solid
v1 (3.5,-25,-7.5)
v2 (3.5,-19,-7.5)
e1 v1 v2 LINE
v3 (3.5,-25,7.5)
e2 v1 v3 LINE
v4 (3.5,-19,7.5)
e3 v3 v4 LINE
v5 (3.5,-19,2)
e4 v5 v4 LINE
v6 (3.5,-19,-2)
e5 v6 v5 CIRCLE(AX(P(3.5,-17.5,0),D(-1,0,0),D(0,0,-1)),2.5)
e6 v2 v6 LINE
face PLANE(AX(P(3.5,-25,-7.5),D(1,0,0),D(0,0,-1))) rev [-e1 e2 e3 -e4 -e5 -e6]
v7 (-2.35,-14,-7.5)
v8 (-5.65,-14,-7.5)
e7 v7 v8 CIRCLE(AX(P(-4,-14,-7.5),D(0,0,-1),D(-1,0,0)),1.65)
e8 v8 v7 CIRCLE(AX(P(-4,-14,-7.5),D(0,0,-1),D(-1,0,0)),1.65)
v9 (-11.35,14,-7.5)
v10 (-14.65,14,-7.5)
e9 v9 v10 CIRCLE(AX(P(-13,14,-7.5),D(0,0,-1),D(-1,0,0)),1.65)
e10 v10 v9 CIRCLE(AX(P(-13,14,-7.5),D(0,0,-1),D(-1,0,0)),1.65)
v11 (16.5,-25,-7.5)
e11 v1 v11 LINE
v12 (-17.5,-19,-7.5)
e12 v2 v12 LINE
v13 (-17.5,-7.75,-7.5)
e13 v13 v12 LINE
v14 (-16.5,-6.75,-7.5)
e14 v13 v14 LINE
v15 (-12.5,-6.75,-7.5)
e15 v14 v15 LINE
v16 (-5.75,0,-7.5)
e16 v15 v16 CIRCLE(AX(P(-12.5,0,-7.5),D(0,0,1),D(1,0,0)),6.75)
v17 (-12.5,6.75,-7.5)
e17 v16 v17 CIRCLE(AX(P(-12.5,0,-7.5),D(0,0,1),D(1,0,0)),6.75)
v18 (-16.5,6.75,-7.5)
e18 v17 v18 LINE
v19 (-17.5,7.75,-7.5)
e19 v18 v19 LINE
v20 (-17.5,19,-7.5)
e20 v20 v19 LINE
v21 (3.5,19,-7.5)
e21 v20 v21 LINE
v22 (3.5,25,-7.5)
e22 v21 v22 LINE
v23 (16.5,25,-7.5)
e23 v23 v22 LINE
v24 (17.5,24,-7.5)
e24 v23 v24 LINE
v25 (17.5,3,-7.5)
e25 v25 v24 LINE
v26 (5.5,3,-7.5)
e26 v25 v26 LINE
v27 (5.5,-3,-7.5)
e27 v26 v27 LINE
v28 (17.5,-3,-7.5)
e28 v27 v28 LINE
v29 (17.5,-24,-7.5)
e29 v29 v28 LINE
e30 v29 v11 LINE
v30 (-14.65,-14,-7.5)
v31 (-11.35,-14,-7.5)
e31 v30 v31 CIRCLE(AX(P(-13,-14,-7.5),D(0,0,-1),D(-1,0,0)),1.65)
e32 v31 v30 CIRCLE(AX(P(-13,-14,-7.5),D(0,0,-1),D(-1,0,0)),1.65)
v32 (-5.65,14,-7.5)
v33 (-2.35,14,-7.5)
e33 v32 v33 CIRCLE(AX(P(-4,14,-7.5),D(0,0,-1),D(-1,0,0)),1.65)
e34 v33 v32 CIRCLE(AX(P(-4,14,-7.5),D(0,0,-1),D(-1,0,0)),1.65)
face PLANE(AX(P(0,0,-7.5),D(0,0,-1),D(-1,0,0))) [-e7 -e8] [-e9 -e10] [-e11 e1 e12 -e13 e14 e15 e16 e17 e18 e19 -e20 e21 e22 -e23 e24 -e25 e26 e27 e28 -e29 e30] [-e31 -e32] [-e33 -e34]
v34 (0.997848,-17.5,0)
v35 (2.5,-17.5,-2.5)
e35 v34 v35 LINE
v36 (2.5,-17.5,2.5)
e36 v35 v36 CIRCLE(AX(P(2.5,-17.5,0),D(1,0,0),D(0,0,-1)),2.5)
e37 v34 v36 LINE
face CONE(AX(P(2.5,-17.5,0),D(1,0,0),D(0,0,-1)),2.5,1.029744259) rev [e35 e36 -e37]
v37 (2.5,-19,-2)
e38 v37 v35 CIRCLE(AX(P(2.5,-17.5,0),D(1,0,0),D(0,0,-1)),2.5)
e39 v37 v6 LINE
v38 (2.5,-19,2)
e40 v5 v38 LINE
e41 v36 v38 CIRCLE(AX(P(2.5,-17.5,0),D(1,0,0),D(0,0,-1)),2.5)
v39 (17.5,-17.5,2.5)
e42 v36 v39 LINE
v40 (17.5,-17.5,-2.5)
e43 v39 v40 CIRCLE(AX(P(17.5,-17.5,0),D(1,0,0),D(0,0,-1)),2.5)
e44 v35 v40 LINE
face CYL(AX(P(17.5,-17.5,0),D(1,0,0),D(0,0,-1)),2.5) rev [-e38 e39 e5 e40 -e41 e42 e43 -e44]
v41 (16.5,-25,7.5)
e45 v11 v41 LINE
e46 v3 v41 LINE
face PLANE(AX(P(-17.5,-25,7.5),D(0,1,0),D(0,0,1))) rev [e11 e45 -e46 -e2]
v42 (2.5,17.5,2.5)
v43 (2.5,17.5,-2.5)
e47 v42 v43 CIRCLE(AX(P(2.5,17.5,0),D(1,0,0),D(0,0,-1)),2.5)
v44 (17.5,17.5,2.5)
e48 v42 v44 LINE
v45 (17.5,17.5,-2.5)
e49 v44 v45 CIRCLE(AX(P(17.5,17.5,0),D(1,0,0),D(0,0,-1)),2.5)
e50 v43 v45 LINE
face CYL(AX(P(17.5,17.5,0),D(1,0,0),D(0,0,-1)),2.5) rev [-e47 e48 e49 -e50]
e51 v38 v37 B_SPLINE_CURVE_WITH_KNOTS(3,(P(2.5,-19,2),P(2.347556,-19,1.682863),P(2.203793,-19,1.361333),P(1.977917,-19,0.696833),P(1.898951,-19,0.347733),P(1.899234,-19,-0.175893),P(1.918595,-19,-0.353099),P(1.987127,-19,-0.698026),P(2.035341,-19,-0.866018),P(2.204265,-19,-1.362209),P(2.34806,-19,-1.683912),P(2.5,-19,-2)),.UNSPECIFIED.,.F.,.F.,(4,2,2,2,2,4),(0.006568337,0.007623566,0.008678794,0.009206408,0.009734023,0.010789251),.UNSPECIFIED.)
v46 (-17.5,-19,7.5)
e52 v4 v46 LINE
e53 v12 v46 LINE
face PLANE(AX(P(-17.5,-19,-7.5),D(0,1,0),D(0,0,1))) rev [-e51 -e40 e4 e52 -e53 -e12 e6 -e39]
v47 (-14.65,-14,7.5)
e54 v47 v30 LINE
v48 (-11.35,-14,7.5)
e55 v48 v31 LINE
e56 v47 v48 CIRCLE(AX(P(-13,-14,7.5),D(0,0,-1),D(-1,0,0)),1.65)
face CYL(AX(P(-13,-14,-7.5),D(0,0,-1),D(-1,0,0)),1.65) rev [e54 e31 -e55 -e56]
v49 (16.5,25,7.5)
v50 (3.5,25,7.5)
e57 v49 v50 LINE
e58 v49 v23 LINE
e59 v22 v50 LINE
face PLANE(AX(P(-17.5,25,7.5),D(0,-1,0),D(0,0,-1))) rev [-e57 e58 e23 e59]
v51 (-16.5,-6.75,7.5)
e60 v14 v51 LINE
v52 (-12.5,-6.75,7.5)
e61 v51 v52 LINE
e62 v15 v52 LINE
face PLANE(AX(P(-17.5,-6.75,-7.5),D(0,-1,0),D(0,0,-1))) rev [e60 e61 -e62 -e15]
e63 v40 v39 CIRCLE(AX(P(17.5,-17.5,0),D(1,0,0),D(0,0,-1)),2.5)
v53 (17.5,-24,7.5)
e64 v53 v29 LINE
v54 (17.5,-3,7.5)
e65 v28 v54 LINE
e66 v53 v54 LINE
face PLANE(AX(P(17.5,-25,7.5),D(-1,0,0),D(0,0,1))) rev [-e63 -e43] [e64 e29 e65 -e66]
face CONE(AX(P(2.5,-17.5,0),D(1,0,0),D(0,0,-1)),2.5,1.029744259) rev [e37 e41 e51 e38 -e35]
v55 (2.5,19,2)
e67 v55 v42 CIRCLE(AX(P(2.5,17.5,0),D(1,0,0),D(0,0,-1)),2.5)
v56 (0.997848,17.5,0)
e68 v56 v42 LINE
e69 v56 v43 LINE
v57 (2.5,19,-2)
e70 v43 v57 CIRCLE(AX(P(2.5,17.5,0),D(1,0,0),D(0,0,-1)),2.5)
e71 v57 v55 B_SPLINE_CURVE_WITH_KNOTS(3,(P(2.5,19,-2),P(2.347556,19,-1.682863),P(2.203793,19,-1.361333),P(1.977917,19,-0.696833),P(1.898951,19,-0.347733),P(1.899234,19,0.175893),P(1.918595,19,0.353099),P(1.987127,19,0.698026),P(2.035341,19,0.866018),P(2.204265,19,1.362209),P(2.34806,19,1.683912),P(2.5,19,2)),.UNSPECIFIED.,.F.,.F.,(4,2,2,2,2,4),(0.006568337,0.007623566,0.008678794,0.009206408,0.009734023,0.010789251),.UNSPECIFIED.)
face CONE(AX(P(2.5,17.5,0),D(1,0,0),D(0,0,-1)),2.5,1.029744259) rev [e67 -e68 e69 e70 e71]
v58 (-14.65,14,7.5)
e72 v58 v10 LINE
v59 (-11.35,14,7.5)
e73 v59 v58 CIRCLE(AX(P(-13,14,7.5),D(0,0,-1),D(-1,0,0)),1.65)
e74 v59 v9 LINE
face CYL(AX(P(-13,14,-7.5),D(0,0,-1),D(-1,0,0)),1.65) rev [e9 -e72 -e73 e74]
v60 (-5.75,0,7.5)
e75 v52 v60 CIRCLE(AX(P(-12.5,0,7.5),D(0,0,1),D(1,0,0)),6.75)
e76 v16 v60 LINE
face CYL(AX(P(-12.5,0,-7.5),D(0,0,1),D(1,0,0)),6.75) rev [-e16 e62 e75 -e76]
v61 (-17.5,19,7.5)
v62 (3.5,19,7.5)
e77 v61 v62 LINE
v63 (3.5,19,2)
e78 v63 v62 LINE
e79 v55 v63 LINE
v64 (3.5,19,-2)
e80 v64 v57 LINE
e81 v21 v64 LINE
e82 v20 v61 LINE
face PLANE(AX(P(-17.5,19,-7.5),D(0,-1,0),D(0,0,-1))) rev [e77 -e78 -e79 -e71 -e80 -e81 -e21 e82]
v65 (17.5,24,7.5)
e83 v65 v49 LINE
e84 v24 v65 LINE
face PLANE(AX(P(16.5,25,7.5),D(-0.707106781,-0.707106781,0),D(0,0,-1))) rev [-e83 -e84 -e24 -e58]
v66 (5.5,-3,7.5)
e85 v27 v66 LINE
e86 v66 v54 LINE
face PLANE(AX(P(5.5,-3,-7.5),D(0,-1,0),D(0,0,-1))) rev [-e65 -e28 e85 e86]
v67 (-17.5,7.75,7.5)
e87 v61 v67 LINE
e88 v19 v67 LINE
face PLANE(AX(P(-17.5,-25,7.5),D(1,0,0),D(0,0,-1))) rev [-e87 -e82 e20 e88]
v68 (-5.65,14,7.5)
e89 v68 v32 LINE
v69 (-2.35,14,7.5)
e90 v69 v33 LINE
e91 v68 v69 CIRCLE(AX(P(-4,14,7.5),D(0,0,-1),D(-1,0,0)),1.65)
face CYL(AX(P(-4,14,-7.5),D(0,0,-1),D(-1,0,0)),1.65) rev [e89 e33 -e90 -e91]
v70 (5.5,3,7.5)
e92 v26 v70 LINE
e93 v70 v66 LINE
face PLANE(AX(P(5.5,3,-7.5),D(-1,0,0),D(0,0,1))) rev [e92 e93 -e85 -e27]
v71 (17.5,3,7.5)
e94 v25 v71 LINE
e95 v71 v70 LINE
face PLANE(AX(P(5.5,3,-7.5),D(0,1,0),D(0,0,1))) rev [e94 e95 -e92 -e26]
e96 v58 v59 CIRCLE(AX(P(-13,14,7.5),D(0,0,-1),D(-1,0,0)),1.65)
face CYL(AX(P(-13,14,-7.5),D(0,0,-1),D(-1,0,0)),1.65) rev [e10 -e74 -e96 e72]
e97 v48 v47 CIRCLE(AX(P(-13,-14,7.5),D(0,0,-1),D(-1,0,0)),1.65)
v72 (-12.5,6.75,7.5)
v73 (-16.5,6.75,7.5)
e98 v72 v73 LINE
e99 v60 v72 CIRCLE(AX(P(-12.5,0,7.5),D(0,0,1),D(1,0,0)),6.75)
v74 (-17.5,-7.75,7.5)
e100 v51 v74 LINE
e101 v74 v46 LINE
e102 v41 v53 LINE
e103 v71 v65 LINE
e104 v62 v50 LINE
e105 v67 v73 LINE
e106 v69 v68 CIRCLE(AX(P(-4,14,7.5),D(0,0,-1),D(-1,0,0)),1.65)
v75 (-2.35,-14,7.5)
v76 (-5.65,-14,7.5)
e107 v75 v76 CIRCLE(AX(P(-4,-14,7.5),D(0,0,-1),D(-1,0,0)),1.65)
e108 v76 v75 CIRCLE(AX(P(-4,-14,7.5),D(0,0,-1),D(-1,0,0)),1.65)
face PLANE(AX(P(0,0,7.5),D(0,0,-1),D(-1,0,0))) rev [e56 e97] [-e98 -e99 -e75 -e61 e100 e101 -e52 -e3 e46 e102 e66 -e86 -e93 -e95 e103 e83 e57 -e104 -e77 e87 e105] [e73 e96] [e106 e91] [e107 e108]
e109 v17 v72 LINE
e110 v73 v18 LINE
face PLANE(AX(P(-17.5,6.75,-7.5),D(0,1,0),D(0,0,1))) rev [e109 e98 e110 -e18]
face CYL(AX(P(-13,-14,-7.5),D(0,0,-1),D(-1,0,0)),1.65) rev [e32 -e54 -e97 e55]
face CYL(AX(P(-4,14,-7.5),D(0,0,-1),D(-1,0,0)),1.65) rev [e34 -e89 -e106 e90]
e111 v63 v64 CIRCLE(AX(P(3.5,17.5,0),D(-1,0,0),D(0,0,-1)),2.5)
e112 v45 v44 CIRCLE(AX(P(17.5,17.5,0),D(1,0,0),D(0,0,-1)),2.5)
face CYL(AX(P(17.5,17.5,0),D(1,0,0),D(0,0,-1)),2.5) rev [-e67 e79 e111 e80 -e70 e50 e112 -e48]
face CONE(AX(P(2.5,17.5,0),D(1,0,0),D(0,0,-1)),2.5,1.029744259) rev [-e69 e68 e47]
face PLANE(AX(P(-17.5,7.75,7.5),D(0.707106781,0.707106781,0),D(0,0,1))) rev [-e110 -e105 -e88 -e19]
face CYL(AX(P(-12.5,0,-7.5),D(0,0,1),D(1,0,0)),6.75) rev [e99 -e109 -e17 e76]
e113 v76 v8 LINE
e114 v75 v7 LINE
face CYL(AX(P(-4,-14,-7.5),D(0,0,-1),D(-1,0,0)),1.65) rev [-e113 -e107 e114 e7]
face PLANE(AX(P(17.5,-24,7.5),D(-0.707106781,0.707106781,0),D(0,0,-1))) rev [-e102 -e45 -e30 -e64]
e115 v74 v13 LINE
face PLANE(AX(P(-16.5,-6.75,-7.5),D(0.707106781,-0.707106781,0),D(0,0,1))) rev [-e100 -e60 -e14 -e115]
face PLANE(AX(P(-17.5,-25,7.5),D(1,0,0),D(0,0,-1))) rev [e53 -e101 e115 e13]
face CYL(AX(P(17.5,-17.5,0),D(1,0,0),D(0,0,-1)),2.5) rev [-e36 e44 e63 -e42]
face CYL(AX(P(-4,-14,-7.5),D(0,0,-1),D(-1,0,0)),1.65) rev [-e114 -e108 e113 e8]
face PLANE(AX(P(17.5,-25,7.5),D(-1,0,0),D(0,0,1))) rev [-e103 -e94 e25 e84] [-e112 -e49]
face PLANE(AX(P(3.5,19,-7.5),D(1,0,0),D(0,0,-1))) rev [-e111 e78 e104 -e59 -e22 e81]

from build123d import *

# Parameters (mm, degrees)
SKETCH_1_W             = 35
SKETCH_1_H             = 50
EXTRUDE_1_DEPTH        = 7.5
CUT_EXTRUDE_1_DEPTH    = 35.003676272
HOLE_WIZARD_M4_2_D     = 3.3
CHAMFER_1_SIZE         = 1
HOLE_WIZARD_M6_1_D     = 5
HOLE_WIZARD_M6_1_DEPTH = 15
HOLE_WIZARD_M6_1_TIP   = 1.502151548
SKETCH_17_W            = 12
SKETCH_17_H            = 6
CUT_EXTRUDE_2_DEPTH    = 35.003676272
SKETCH_19_W            = 21
SKETCH_19_H            = 6
CUT_EXTRUDE_8_DEPTH    = 35.003676272


with BuildPart() as part:
    # 草图1 → 凸台-拉伸1 (new, symmetric)
    with BuildSketch(Plane.XY):
        Rectangle(SKETCH_1_W, SKETCH_1_H)
    extrude(amount=EXTRUDE_1_DEPTH, both=True)

    # 草图2 → 切除-拉伸1 (cut, through all)
    with BuildSketch(Plane.XY.offset(7.5)):
        with BuildLine():
            Line((-17.5, 6.75), (-12.5, 6.75))
            ThreePointArc((-12.5, 6.75), (-5.75, 0), (-12.5, -6.75))
            Line((-12.5, -6.75), (-17.5, -6.75))
            ThreePointArc((-17.5, -6.75), (-24.25, 0), (-17.5, 6.75))
        make_face()
    extrude(amount=-CUT_EXTRUDE_1_DEPTH, mode=Mode.SUBTRACT)

    # M4 螺纹孔2 (through all)
    with Locations(Plane(origin=(0, 0, -7.5), x_dir=(-1, 0, 0), z_dir=(0, 0, -1))):
        with Locations((4, -14), (13, -14), (4, 14), (13, 14)):
            Hole(HOLE_WIZARD_M4_2_D / 2)

    # 倒角1
    chamfer_1_edges = [part.edges().sort_by_distance(p)[0] for p in [
        (-17.5, -6.75, 0),
        (-17.5, 6.75, 0),
        (17.5, -25, 0),
        (17.5, 25, 0),
    ]]
    chamfer(chamfer_1_edges, length=CHAMFER_1_SIZE)

    # M6 螺纹孔1
    with Locations(Plane(origin=(17.5, 0, 0), x_dir=(0, 0, -1), z_dir=(1, 0, 0))):
        with Locations((0, -17.5), (0, 17.5)):
            Hole(HOLE_WIZARD_M6_1_D / 2, depth=HOLE_WIZARD_M6_1_DEPTH)
            with Locations((0, 0, -(HOLE_WIZARD_M6_1_DEPTH + HOLE_WIZARD_M6_1_TIP / 2))):  # 118° drill point
                Cone(0, HOLE_WIZARD_M6_1_D / 2, HOLE_WIZARD_M6_1_TIP, mode=Mode.SUBTRACT)

    # 草图17 → 切除-拉伸2 (cut, through all)
    with BuildSketch(Plane.XY.offset(7.5)):
        with Locations((11.5, 0)):
            Rectangle(SKETCH_17_W, SKETCH_17_H)
    extrude(amount=-CUT_EXTRUDE_2_DEPTH, mode=Mode.SUBTRACT)

    # 草图19 → 切除-拉伸8 (cut, through all)
    with BuildSketch(Plane.XY.offset(7.5)):
        with Locations((-7, -22)):
            Rectangle(SKETCH_19_W, SKETCH_19_H)
        with Locations((-7, 22)):
            Rectangle(SKETCH_19_W, SKETCH_19_H)
    extrude(amount=-CUT_EXTRUDE_8_DEPTH, mode=Mode.SUBTRACT)


solid = part.part
